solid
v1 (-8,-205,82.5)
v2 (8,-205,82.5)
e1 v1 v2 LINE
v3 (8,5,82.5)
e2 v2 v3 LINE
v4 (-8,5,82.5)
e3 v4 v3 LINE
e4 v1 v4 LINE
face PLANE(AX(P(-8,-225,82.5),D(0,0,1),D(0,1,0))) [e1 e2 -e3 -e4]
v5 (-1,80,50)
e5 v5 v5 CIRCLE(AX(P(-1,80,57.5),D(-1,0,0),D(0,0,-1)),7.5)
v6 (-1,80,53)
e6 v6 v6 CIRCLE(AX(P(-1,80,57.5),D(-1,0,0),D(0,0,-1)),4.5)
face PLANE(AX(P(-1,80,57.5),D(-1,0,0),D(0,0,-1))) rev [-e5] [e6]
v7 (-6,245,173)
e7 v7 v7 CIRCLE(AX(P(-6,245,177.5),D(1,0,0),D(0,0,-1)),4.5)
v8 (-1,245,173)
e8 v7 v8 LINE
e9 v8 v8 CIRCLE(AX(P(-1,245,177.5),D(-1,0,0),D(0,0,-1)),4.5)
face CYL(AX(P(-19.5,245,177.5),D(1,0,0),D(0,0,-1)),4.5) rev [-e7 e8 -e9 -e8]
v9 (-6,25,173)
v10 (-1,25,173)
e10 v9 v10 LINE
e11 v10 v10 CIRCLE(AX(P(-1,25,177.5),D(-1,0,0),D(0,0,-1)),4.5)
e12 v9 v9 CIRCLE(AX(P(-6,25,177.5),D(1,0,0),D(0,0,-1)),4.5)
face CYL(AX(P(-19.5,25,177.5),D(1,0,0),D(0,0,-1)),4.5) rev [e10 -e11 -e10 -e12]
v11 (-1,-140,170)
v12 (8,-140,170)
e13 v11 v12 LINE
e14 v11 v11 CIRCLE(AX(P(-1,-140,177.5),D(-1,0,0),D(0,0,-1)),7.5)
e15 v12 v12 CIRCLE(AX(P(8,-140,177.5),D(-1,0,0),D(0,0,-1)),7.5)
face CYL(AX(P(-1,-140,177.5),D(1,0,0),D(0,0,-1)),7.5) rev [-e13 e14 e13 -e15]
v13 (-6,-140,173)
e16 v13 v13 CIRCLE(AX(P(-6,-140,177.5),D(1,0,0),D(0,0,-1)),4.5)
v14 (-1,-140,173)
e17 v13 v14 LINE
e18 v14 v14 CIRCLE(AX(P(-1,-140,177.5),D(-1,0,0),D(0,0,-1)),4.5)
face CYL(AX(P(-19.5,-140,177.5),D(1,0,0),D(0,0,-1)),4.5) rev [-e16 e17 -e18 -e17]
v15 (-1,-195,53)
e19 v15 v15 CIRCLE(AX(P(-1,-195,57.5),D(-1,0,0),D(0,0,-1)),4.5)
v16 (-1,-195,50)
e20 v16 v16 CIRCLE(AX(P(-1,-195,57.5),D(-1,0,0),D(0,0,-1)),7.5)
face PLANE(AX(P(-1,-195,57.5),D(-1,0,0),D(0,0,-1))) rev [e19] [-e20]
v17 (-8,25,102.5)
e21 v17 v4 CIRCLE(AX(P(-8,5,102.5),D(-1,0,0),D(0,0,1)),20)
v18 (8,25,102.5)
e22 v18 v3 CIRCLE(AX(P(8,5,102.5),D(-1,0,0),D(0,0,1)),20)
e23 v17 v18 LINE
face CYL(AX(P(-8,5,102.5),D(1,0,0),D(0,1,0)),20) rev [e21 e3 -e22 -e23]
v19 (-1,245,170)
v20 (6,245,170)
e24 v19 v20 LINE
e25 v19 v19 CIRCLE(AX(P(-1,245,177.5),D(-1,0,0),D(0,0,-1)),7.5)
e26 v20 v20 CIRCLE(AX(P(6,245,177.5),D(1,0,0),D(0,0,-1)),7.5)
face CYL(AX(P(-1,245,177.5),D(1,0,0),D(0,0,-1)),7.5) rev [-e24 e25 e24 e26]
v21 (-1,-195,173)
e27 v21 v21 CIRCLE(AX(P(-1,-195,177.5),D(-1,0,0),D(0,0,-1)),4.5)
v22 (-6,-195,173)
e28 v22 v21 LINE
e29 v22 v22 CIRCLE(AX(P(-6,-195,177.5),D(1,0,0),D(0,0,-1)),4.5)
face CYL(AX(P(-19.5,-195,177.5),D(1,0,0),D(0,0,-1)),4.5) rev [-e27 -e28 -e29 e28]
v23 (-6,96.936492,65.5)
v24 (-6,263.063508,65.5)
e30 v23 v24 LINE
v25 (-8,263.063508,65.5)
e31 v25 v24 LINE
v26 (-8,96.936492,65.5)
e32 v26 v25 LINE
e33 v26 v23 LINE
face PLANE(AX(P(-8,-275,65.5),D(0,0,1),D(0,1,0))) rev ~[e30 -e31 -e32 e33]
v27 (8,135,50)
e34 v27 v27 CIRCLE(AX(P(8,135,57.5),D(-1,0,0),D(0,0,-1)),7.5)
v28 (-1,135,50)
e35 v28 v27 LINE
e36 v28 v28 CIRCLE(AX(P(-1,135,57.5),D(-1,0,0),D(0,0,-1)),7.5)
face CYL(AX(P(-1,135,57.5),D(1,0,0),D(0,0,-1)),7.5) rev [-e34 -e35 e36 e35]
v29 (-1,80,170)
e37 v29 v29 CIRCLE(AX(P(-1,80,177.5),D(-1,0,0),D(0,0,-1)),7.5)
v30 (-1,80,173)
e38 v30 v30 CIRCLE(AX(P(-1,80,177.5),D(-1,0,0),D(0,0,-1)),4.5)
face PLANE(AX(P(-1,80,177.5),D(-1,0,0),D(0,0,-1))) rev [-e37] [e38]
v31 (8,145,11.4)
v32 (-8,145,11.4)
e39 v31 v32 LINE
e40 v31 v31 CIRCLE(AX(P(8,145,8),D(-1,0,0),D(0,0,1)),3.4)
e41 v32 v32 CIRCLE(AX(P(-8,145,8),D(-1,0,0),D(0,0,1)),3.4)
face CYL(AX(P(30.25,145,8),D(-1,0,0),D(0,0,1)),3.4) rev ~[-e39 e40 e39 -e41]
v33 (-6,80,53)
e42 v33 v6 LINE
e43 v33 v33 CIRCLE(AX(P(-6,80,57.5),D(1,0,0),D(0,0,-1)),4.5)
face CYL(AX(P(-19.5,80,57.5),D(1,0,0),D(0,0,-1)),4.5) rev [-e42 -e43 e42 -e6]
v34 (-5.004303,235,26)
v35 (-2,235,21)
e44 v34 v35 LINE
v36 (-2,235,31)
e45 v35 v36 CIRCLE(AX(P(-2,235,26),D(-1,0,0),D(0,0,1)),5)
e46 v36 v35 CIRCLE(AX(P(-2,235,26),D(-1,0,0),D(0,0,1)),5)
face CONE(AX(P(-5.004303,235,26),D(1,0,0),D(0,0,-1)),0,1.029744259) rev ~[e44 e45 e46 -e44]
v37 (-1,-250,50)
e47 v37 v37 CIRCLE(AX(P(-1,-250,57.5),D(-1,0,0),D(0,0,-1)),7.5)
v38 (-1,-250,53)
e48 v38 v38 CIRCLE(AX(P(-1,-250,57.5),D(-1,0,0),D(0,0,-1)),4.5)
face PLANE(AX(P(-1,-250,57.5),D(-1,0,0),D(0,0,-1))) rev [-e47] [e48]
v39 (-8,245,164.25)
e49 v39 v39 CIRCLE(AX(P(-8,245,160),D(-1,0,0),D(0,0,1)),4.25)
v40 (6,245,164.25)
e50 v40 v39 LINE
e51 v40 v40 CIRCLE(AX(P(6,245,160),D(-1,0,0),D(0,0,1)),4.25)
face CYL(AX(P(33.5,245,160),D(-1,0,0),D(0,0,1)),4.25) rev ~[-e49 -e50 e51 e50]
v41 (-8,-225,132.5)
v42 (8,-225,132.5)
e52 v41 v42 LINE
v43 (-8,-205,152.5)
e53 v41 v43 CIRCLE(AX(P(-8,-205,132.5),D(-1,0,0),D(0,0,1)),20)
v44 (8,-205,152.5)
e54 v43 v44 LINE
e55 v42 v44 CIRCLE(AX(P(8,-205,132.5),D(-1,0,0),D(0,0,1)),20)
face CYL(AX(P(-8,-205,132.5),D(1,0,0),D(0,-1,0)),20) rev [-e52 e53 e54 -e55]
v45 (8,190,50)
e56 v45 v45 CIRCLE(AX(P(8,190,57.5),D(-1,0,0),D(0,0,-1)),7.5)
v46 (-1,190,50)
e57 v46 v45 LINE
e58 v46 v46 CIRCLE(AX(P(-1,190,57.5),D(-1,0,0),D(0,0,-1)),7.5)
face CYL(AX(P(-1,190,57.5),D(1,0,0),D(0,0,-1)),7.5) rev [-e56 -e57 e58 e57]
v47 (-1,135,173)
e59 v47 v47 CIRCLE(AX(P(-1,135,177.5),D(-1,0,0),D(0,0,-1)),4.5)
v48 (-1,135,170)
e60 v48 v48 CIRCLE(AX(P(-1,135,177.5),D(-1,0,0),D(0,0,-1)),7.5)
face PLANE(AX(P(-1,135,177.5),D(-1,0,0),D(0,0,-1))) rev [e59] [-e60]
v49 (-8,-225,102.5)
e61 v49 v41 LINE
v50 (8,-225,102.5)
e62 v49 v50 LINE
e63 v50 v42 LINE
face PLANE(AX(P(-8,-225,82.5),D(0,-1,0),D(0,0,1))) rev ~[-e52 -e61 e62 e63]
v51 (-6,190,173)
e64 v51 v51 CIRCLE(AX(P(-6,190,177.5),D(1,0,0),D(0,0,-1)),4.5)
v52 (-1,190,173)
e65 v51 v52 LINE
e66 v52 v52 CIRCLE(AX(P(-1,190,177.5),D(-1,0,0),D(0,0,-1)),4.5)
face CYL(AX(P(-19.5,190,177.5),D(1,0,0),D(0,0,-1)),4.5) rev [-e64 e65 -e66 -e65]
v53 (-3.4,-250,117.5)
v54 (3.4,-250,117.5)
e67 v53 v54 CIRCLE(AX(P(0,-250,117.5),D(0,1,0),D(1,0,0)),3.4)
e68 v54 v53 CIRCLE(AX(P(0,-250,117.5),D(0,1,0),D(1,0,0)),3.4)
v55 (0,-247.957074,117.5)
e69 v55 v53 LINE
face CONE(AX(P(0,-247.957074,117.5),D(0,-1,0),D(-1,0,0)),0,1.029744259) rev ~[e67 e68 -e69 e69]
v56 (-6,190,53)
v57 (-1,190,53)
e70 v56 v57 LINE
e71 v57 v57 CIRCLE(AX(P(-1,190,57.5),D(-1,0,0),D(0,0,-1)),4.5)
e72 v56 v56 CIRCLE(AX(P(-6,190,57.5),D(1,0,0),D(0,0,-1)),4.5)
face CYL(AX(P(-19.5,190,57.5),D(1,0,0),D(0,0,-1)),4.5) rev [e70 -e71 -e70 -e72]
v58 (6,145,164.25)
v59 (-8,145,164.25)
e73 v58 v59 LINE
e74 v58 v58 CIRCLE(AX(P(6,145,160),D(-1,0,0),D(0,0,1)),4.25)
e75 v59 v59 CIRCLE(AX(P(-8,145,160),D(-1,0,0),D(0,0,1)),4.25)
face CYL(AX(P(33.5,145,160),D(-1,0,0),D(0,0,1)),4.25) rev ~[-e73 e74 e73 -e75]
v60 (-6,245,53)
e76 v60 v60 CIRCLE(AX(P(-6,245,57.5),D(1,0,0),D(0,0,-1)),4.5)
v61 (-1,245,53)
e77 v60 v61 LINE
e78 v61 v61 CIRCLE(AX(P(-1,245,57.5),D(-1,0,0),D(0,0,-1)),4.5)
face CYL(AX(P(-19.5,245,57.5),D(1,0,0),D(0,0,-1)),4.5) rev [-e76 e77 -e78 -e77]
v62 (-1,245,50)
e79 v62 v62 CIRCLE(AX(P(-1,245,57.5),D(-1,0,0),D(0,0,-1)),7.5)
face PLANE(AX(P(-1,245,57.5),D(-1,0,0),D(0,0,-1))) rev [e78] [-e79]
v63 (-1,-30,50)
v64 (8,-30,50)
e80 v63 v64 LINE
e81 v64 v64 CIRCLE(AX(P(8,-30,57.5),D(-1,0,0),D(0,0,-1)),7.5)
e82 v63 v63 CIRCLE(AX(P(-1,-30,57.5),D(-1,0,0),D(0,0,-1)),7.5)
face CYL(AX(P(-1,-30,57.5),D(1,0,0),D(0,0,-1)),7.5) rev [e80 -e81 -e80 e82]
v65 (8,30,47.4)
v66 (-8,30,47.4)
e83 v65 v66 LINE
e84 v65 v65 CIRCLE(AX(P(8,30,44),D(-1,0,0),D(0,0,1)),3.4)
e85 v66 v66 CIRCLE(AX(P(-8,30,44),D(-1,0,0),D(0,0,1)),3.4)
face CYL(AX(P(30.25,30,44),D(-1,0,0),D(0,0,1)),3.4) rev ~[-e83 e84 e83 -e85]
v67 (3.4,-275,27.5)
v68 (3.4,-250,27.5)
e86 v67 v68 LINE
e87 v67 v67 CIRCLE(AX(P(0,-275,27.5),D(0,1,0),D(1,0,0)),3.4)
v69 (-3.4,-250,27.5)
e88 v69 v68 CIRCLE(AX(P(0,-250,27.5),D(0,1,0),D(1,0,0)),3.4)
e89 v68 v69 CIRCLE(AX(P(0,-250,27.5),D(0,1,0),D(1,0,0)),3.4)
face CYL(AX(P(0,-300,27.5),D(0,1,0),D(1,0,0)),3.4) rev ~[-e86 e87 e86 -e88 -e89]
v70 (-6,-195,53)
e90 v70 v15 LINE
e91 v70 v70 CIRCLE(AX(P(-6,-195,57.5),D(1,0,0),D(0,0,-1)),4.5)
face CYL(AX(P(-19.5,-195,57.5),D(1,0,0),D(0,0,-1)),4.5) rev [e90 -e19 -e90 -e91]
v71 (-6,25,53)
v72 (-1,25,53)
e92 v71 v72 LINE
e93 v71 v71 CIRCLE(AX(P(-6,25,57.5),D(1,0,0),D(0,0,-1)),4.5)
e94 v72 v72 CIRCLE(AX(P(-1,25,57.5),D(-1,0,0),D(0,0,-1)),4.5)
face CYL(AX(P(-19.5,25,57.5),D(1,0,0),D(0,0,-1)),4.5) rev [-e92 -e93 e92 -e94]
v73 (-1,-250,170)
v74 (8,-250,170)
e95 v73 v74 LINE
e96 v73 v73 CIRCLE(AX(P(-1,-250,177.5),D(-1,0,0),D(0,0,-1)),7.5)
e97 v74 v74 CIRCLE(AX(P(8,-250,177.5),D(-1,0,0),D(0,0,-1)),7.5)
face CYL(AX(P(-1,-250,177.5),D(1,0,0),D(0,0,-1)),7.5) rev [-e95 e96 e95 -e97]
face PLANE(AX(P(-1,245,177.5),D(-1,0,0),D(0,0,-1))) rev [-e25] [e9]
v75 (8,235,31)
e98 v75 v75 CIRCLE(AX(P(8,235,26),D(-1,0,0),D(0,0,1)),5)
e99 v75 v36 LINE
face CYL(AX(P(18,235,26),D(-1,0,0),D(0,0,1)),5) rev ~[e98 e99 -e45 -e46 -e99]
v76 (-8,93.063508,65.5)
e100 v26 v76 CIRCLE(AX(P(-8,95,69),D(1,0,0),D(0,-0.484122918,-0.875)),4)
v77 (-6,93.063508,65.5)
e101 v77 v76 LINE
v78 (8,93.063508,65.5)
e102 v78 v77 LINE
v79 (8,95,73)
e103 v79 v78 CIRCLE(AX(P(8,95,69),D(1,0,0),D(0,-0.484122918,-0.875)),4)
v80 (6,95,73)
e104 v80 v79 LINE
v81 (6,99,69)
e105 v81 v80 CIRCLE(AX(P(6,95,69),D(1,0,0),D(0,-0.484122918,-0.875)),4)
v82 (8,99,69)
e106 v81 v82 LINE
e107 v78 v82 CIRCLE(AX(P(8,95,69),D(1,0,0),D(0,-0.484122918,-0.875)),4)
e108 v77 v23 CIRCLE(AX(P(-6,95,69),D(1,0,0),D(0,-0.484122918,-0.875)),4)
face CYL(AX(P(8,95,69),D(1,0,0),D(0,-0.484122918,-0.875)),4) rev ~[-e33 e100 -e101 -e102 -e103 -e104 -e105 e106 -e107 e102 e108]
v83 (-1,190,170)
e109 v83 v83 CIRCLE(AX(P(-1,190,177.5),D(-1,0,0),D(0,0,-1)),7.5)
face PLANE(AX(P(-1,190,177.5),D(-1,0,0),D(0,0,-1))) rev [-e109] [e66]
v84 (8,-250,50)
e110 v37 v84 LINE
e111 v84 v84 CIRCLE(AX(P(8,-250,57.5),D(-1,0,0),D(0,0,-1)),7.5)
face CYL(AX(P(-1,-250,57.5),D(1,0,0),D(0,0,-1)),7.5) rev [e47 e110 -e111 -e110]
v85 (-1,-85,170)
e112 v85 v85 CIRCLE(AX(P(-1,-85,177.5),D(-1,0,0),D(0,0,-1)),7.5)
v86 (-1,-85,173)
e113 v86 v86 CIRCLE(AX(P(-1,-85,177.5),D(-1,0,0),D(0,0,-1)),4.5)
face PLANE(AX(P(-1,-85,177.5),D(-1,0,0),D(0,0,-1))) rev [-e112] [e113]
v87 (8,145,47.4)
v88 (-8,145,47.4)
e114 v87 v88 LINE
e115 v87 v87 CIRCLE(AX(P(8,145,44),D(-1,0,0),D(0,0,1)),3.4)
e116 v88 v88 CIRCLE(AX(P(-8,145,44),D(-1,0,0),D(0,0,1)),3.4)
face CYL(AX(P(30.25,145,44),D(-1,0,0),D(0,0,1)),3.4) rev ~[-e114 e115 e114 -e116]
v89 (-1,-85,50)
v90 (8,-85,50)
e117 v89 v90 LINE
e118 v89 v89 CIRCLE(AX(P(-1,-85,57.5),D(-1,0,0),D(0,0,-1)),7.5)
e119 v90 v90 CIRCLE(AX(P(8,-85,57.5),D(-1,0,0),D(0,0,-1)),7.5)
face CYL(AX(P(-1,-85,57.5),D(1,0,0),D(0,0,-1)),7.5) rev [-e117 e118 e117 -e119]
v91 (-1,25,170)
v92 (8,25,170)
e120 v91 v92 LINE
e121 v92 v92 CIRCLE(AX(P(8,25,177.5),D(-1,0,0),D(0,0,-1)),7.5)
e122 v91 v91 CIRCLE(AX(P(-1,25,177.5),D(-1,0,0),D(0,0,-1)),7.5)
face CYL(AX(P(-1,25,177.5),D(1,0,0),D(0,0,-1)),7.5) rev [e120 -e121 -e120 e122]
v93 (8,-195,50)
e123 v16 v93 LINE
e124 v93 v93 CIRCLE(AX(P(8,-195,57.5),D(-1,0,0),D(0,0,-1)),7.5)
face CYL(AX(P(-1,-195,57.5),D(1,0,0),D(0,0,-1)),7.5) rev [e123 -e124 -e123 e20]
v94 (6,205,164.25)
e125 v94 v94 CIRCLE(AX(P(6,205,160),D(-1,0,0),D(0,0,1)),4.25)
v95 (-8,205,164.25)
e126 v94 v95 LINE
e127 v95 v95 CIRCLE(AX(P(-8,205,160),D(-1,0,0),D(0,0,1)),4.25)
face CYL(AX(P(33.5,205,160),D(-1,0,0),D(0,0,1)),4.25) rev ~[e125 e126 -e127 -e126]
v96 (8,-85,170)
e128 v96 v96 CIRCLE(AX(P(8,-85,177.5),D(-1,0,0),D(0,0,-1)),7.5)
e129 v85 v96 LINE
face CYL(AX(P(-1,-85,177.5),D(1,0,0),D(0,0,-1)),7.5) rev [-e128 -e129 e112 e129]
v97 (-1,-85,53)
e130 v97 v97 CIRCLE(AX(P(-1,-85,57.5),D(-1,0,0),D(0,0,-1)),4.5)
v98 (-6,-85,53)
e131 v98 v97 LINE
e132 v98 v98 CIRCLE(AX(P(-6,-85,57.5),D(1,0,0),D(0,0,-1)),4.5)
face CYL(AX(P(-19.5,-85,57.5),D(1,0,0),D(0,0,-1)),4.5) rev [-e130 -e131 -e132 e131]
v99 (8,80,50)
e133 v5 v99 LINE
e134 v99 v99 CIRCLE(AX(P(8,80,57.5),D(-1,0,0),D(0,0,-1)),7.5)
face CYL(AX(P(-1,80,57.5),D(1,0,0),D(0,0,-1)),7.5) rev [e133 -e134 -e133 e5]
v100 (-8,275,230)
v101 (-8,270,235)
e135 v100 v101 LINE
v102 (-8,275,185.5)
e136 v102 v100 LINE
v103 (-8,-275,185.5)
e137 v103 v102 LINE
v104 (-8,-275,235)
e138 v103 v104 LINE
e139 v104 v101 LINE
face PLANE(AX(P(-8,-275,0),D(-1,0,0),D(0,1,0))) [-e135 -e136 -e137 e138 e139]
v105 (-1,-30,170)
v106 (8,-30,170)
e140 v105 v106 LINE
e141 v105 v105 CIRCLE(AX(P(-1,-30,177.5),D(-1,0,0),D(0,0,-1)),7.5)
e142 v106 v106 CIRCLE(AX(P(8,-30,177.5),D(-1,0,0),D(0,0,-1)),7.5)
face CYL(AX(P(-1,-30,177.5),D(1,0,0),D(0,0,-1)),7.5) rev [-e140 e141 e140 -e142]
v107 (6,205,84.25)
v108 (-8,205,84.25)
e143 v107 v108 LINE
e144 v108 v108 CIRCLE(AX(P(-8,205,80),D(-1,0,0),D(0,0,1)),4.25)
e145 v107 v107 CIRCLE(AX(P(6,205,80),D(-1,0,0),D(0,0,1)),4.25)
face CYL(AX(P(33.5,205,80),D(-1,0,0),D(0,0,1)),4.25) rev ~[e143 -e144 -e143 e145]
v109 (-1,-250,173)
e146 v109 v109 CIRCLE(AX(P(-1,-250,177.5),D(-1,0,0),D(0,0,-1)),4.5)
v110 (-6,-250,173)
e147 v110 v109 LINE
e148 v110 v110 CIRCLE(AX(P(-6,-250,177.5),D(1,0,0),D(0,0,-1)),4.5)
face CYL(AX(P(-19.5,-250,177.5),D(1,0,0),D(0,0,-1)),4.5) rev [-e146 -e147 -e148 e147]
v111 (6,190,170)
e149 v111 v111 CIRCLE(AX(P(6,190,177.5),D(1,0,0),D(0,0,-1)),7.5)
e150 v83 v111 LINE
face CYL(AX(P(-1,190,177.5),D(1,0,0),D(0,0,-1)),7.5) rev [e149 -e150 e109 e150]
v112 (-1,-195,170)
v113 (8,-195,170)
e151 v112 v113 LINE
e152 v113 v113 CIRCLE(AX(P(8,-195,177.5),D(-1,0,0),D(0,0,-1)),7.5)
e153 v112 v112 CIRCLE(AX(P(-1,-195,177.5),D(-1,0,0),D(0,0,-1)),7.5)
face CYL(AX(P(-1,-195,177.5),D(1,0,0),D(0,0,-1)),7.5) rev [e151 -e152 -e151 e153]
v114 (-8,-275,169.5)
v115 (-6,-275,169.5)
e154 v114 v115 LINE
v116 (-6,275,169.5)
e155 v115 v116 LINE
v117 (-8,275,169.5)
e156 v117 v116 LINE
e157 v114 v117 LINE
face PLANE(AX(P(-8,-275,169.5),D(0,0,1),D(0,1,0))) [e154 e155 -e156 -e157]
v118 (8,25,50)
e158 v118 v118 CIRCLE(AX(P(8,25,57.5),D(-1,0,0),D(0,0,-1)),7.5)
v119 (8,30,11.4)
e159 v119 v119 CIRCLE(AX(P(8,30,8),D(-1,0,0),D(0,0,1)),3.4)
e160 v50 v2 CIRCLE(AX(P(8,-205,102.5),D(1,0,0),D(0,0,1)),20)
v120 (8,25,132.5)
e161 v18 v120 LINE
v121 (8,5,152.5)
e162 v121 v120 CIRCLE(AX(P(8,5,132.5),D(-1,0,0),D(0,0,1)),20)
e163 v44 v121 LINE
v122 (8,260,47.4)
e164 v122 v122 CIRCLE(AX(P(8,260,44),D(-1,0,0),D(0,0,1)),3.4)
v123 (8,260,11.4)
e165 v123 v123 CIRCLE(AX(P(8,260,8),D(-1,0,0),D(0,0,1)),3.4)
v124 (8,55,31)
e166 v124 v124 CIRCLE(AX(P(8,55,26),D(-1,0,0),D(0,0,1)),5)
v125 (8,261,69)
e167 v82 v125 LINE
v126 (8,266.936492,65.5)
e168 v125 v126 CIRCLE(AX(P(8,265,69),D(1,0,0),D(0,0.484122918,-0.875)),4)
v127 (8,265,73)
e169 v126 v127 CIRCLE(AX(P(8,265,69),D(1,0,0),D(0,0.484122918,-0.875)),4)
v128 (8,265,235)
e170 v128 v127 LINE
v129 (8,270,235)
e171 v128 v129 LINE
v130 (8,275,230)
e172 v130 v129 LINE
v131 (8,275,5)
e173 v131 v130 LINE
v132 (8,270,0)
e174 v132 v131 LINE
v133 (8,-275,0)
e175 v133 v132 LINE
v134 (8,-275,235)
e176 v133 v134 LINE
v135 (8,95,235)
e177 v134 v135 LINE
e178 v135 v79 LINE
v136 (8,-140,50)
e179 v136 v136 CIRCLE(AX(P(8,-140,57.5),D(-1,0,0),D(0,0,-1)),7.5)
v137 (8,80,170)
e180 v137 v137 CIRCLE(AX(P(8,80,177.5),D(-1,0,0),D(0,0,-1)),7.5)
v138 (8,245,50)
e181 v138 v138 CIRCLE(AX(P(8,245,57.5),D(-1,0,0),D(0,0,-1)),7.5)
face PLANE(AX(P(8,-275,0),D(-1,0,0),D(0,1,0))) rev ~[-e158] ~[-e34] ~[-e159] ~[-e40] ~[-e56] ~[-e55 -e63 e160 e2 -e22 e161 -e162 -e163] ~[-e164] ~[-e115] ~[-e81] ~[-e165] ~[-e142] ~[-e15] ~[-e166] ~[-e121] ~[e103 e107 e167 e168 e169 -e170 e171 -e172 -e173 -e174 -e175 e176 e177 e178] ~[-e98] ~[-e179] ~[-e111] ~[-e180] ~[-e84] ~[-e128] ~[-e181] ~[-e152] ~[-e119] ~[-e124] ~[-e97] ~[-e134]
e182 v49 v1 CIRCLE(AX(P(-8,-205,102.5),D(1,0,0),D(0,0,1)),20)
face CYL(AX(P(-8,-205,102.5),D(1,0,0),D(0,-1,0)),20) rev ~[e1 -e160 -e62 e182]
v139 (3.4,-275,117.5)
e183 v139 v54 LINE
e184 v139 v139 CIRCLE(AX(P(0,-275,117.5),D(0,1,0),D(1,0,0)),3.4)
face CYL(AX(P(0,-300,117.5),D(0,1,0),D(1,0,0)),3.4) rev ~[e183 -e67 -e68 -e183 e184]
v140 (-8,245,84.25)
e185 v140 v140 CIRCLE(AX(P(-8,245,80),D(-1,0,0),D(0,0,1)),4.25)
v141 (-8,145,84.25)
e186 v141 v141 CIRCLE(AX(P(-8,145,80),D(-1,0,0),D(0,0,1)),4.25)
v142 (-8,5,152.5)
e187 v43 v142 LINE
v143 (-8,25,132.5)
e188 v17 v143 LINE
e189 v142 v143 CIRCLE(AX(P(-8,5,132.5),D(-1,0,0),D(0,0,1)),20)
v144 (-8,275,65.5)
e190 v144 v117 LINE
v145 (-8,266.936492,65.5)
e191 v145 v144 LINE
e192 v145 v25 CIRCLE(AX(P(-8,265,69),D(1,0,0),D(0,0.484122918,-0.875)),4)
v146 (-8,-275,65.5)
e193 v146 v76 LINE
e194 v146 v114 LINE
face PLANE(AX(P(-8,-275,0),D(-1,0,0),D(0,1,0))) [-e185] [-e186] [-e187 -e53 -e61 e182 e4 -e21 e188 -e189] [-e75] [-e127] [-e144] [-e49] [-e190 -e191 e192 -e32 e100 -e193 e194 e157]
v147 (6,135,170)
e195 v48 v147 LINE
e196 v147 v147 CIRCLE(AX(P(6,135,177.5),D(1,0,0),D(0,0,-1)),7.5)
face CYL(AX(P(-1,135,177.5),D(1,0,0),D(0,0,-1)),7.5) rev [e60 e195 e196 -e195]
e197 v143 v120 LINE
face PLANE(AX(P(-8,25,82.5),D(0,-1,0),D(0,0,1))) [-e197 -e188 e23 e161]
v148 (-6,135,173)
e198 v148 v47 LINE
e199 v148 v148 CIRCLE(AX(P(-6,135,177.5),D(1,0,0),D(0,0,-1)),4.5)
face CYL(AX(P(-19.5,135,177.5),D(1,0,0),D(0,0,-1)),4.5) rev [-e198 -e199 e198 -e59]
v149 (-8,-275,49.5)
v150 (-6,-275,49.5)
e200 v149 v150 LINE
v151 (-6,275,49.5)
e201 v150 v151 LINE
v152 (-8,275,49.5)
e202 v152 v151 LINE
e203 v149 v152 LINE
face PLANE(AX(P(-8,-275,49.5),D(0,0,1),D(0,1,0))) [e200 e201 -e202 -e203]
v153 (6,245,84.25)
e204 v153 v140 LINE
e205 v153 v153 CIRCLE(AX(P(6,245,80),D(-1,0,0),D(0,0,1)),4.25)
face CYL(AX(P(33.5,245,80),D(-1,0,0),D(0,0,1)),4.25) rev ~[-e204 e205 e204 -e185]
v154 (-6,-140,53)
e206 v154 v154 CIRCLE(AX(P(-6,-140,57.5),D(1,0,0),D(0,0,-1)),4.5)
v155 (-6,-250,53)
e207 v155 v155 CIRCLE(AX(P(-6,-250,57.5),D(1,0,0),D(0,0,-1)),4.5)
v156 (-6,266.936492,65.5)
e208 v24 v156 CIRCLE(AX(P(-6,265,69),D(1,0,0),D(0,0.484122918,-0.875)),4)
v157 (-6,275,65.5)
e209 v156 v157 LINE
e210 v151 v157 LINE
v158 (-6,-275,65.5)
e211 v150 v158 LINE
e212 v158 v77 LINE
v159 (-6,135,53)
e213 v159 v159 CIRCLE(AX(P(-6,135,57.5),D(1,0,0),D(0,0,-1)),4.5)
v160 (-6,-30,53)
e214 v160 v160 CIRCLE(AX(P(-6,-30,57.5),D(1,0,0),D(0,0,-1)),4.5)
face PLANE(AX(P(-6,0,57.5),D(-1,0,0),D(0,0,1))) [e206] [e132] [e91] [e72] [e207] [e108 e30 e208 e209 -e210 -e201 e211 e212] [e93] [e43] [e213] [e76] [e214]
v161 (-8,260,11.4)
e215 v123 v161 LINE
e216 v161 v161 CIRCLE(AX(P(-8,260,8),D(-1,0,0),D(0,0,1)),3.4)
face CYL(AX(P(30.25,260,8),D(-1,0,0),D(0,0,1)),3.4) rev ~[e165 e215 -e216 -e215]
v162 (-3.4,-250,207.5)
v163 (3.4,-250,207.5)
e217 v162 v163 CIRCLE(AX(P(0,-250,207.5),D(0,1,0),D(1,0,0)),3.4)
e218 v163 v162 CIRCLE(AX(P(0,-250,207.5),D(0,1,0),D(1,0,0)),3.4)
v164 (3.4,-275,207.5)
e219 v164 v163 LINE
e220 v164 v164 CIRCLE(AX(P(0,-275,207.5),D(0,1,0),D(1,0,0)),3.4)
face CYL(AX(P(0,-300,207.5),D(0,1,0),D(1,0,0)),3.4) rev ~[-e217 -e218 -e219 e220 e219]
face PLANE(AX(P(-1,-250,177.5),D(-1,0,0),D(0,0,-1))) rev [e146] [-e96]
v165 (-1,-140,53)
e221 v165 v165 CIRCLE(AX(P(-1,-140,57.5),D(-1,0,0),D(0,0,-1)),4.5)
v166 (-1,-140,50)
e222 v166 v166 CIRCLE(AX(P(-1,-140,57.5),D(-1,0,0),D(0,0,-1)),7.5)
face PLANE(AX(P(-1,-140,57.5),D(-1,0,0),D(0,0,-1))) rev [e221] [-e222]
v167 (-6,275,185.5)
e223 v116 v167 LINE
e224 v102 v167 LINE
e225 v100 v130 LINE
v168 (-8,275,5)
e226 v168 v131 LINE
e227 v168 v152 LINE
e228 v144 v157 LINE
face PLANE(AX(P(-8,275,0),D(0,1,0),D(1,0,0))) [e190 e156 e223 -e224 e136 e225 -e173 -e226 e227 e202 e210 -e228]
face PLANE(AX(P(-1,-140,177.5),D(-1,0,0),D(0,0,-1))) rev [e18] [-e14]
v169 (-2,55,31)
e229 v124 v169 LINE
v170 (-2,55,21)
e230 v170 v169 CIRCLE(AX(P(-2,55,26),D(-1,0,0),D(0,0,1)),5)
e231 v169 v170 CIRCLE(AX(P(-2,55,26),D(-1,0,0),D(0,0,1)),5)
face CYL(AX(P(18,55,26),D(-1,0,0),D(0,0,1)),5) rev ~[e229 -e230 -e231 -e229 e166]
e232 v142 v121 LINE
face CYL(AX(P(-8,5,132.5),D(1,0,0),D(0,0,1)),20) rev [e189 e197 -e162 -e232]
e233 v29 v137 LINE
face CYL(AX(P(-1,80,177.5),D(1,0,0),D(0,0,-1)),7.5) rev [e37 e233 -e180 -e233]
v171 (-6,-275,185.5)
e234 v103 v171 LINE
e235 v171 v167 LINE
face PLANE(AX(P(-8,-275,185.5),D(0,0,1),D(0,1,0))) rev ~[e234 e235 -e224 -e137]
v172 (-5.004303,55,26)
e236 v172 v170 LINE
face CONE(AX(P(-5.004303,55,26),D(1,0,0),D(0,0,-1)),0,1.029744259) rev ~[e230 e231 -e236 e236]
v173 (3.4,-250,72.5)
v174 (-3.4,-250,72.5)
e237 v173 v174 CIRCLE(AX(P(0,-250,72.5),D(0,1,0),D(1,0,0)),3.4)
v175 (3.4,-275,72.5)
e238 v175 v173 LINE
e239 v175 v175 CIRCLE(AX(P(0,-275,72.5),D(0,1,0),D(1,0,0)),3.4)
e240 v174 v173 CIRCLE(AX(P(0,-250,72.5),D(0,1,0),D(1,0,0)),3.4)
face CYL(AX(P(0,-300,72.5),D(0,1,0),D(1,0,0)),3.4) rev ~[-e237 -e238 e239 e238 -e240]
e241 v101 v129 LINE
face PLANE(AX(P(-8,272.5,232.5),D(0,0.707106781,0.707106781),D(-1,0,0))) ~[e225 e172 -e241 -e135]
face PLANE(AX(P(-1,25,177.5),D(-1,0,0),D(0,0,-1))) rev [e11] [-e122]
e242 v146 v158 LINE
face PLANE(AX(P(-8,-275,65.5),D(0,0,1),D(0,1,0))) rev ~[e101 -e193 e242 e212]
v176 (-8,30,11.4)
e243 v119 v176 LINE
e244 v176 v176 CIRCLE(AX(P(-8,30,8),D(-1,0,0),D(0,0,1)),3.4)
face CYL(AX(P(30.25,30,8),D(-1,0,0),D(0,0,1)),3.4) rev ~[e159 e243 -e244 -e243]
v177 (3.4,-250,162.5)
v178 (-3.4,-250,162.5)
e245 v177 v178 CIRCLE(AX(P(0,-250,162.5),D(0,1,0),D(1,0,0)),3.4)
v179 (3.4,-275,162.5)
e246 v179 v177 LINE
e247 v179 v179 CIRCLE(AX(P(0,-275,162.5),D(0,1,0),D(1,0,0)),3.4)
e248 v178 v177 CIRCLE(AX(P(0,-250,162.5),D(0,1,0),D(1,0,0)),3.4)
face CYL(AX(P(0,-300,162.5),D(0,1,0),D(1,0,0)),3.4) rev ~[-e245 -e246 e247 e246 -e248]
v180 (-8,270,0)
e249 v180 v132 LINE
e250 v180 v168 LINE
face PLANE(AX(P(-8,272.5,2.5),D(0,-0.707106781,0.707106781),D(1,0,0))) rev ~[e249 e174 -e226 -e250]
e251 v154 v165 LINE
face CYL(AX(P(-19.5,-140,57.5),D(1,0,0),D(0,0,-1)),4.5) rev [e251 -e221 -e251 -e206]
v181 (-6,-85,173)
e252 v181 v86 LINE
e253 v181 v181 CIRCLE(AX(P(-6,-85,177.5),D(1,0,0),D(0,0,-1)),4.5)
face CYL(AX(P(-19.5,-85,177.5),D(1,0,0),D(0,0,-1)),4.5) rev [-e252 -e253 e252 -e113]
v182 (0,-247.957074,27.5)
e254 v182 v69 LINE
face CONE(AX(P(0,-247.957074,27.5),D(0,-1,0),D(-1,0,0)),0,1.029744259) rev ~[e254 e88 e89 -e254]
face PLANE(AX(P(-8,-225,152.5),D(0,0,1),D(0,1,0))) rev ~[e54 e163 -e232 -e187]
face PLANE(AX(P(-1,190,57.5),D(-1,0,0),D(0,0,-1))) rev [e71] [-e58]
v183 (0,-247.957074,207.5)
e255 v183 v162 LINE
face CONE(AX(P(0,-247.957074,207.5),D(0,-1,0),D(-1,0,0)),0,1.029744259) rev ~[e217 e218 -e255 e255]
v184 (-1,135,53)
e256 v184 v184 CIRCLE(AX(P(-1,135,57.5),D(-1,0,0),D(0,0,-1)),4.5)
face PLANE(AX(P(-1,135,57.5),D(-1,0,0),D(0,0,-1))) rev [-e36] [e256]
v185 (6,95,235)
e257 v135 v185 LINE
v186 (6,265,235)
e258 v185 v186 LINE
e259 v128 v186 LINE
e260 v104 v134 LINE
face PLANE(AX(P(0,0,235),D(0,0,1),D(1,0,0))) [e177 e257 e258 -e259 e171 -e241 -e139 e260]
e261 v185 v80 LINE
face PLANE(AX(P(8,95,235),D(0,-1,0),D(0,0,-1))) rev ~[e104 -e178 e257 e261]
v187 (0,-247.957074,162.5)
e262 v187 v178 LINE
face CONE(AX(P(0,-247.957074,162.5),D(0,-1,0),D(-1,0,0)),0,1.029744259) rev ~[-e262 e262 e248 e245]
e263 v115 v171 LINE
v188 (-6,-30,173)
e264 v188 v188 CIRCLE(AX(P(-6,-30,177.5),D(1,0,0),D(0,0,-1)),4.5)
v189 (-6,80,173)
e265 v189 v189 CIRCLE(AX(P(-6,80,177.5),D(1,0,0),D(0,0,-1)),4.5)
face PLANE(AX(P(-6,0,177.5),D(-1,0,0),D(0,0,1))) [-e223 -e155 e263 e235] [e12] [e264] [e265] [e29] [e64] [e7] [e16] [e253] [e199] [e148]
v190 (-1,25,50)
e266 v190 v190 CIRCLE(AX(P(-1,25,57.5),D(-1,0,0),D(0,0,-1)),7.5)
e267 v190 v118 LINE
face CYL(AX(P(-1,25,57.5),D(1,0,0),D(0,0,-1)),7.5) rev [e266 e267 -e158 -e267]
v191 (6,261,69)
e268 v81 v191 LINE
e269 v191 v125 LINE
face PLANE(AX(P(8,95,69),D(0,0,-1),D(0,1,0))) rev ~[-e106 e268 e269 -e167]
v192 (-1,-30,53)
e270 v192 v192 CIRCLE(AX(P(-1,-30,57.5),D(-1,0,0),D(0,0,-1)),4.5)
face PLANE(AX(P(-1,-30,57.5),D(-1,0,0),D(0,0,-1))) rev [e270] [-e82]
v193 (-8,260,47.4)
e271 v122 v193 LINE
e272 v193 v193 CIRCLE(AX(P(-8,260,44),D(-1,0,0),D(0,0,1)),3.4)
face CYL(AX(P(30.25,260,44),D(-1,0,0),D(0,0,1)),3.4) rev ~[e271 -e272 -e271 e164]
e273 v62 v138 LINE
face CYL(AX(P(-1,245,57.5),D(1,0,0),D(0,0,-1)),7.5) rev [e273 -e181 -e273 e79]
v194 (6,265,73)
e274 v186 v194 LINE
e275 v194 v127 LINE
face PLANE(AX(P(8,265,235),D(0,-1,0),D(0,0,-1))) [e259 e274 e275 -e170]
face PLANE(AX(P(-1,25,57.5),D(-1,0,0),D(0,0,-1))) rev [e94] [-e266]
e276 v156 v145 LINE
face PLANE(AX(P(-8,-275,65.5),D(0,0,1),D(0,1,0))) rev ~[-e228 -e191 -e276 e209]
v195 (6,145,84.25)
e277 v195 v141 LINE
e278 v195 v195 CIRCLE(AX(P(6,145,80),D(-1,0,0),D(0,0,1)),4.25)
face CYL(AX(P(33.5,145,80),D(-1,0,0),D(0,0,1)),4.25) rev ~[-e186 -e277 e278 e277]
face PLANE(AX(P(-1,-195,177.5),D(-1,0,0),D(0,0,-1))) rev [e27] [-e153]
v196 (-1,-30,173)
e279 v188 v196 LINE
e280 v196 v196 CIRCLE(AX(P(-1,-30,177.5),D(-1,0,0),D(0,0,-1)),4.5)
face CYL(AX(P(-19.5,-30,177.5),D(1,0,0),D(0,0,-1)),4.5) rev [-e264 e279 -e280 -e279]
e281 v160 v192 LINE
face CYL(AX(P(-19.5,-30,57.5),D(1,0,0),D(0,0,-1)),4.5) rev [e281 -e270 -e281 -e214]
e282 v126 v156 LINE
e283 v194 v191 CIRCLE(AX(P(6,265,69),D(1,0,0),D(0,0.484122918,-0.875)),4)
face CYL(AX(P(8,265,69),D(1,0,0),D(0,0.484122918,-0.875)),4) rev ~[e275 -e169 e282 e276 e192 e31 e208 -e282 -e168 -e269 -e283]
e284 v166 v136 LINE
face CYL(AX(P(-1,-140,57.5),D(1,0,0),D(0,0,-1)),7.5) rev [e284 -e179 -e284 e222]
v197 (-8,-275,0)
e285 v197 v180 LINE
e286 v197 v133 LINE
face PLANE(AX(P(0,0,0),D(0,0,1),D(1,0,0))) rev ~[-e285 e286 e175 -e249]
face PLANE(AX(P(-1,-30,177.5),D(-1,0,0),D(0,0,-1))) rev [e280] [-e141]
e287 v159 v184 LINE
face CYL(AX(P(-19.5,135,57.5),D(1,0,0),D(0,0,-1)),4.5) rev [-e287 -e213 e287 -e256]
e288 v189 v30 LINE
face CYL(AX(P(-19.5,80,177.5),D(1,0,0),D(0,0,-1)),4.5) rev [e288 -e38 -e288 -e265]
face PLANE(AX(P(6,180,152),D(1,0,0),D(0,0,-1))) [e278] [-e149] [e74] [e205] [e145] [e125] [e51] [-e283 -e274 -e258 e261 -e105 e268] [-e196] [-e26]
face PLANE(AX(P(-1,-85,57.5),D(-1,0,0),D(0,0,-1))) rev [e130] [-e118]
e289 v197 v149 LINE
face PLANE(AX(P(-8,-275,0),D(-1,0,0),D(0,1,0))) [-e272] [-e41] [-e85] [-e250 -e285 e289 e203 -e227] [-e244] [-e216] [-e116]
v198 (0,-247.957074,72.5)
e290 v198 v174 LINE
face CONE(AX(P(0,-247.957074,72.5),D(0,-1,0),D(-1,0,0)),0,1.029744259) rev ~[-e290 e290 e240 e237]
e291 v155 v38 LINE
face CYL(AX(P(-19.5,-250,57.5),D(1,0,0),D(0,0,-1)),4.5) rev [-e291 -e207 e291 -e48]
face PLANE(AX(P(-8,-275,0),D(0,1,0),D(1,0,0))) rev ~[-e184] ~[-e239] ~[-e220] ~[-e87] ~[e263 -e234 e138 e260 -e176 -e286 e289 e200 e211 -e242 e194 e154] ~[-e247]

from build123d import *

# Parameters (mm, degrees)
SKETCH_1_W               = 16
SKETCH_1_H               = 550
EXTRUDE_1_DEPTH          = 235
SKETCH_4_W               = 16
SKETCH_4_H               = 550
CUT_EXTRUDE_3_DEPTH      = 2
SKETCH_5_W               = 166
SKETCH_5_H               = 170
CUT_EXTRUDE_4_DEPTH      = 2
HOLE_WIZARD_M10_1_D      = 8.5
HOLE_WIZARD_M10_1_DEPTH  = 27.5
HOLE_WIZARD_M10_1_TIP    = 2.553657631
HOLE_WIZARD_M8_1_D       = 6.8
HOLE_WIZARD_M8_1_DEPTH   = 25
HOLE_WIZARD_M8_1_TIP     = 2.042926105
SKETCH_15_W              = 70
SKETCH_15_H              = 250
CUT_EXTRUDE_5_DEPTH      = 16
FILLET_1_R               = 20
CHAMFER_1_SIZE           = 5
HOLE_WIZARD_1_AT_2_COUNT = 2
HOLE_WIZARD_1_AT_2_PITCH = 120
PATTERN_LINEAR_1_COUNT   = 10
PATTERN_LINEAR_1_PITCH   = 55
HOLE_WIZARD_M8_2_D       = 6.8
HOLE_WIZARD_M8_2_DEPTH   = 22.25
HOLE_WIZARD_M8_2_TIP     = 2.042926105
SKETCH_20_R              = 4
CUT_EXTRUDE_6_DEPTH      = 363.085625232
MM_1_D                   = 10
MM_1_DEPTH               = 10
MM_1_TIP                 = 3.004303095


with BuildPart() as part:
    # 草图1 → 凸台-拉伸1 (new body)
    with BuildSketch(Plane.XY):
        Rectangle(SKETCH_1_W, SKETCH_1_H)
    extrude(amount=EXTRUDE_1_DEPTH)

    # 草图4 → 切除-拉伸3 (cut)
    with BuildSketch(Plane.ZY.offset(8)):
        with Locations((57.5, 0)):
            Rectangle(SKETCH_4_W, SKETCH_4_H)
        with Locations((177.5, 0)):
            Rectangle(SKETCH_4_W, SKETCH_4_H)
    extrude(amount=-CUT_EXTRUDE_3_DEPTH, mode=Mode.SUBTRACT)

    # 草图5 → 切除-拉伸4 (cut)
    with BuildSketch(Plane(origin=(8, 0, 0), x_dir=(0, 0, -1), z_dir=(1, 0, 0))):
        with Locations((-152, 180)):
            Rectangle(SKETCH_5_W, SKETCH_5_H)
    extrude(amount=-CUT_EXTRUDE_4_DEPTH, mode=Mode.SUBTRACT)

    # M10 螺纹孔1
    with Locations(Plane(origin=(6, 0, 0), x_dir=(0, 0, -1), z_dir=(1, 0, 0))):
        with Locations((-160, 245), (-80, 145), (-160, 145), (-80, 245), (-80, 205), (-160, 205)):
            Hole(HOLE_WIZARD_M10_1_D / 2, depth=HOLE_WIZARD_M10_1_DEPTH)
            with Locations((0, 0, -(HOLE_WIZARD_M10_1_DEPTH + HOLE_WIZARD_M10_1_TIP / 2))):  # 118° drill point
                Cone(0, HOLE_WIZARD_M10_1_D / 2, HOLE_WIZARD_M10_1_TIP, mode=Mode.SUBTRACT)

    # M8 螺纹孔1
    with Locations(Plane(origin=(0, -275, 0), x_dir=(-1, 0, 0), z_dir=(0, -1, 0))):
        with Locations((0, -207.5), (0, -72.5), (0, -27.5), (0, -117.5), (0, -162.5)):
            Hole(HOLE_WIZARD_M8_1_D / 2, depth=HOLE_WIZARD_M8_1_DEPTH)
            with Locations((0, 0, -(HOLE_WIZARD_M8_1_DEPTH + HOLE_WIZARD_M8_1_TIP / 2))):  # 118° drill point
                Cone(0, HOLE_WIZARD_M8_1_D / 2, HOLE_WIZARD_M8_1_TIP, mode=Mode.SUBTRACT)

    # 草图15 → 切除-拉伸5 (cut)
    with BuildSketch(Plane.ZY.offset(8)):
        with Locations((117.5, -100)):
            Rectangle(SKETCH_15_W, SKETCH_15_H)
    extrude(amount=-CUT_EXTRUDE_5_DEPTH, mode=Mode.SUBTRACT)

    # 圆角1
    fillet_1_edges = [part.edges().sort_by_distance(p)[0] for p in [
        (0, 25, 152.5),
        (0, -225, 152.5),
        (0, -225, 82.5),
        (0, 25, 82.5),
    ]]
    fillet(fillet_1_edges, radius=FILLET_1_R)

    # 倒角1
    chamfer_1_edges = [part.edges().sort_by_distance(p)[0] for p in [
        (0, 275, 0),
        (0, 275, 235),
    ]]
    chamfer(chamfer_1_edges, length=CHAMFER_1_SIZE)

    # 草图17 → 打孔尺寸(%根据)内六角圆柱头螺钉的类型1 (revolve, cut)
    with BuildSketch(Plane(origin=(8, -250, 57.5), x_dir=(0, 0, -1), z_dir=(0, 1, 0))):
        Polygon((0, 0), (0, 30.203872786), (4.5, 27.5), (4.5, 9), (7.5, 9), (7.5, 0), align=None)
    hole_wizard_1 = revolve(axis=Axis((14.35, -250, 57.5), (-1, 0, 0)), mode=Mode.SUBTRACT)

    # 打孔尺寸(%根据)内六角圆柱头螺钉的类型1 at 2: 打孔尺寸(%根据)内六角圆柱头螺钉的类型1 ×2
    with Locations(*[(0, 0, i * HOLE_WIZARD_1_AT_2_PITCH) for i in range(1, HOLE_WIZARD_1_AT_2_COUNT)]):
        add(hole_wizard_1, mode=Mode.SUBTRACT)

    # 阵列(线性)1: 打孔尺寸(%根据)内六角圆柱头螺钉的类型1 ×10
    with Locations(*[(0, i * PATTERN_LINEAR_1_PITCH, 0) for i in range(1, PATTERN_LINEAR_1_COUNT)]):
        add(hole_wizard_1, mode=Mode.SUBTRACT)

    # 阵列(线性)1 copy 1 sketch → 阵列(线性)1 copy 1 (revolve, cut)
    with BuildSketch(Plane(origin=(8, -195, 177.5), x_dir=(0, 0, -1), z_dir=(0, 1, 0))):
        Polygon((0, 0), (0, 30.203872786), (4.5, 27.5), (4.5, 9), (7.5, 9), (7.5, 0), align=None)
    revolve(axis=Axis((14.35, -195, 177.5), (-1, 0, 0)), mode=Mode.SUBTRACT)

    # 阵列(线性)1 copy 2 sketch → 阵列(线性)1 copy 2 (revolve, cut)
    with BuildSketch(Plane(origin=(8, -140, 177.5), x_dir=(0, 0, -1), z_dir=(0, 1, 0))):
        Polygon((0, 0), (0, 30.203872786), (4.5, 27.5), (4.5, 9), (7.5, 9), (7.5, 0), align=None)
    revolve(axis=Axis((14.35, -140, 177.5), (-1, 0, 0)), mode=Mode.SUBTRACT)

    # 阵列(线性)1 copy 3 sketch → 阵列(线性)1 copy 3 (revolve, cut)
    with BuildSketch(Plane(origin=(8, -85, 177.5), x_dir=(0, 0, -1), z_dir=(0, 1, 0))):
        Polygon((0, 0), (0, 30.203872786), (4.5, 27.5), (4.5, 9), (7.5, 9), (7.5, 0), align=None)
    revolve(axis=Axis((14.35, -85, 177.5), (-1, 0, 0)), mode=Mode.SUBTRACT)

    # 阵列(线性)1 copy 4 sketch → 阵列(线性)1 copy 4 (revolve, cut)
    with BuildSketch(Plane(origin=(8, -30, 177.5), x_dir=(0, 0, -1), z_dir=(0, 1, 0))):
        Polygon((0, 0), (0, 30.203872786), (4.5, 27.5), (4.5, 9), (7.5, 9), (7.5, 0), align=None)
    revolve(axis=Axis((14.35, -30, 177.5), (-1, 0, 0)), mode=Mode.SUBTRACT)

    # 阵列(线性)1 copy 5 sketch → 阵列(线性)1 copy 5 (revolve, cut)
    with BuildSketch(Plane(origin=(8, 25, 177.5), x_dir=(0, 0, -1), z_dir=(0, 1, 0))):
        Polygon((0, 0), (0, 30.203872786), (4.5, 27.5), (4.5, 9), (7.5, 9), (7.5, 0), align=None)
    revolve(axis=Axis((14.35, 25, 177.5), (-1, 0, 0)), mode=Mode.SUBTRACT)

    # 阵列(线性)1 copy 6 sketch → 阵列(线性)1 copy 6 (revolve, cut)
    with BuildSketch(Plane(origin=(8, 80, 177.5), x_dir=(0, 0, -1), z_dir=(0, 1, 0))):
        Polygon((0, 0), (0, 30.203872786), (4.5, 27.5), (4.5, 9), (7.5, 9), (7.5, 0), align=None)
    revolve(axis=Axis((14.35, 80, 177.5), (-1, 0, 0)), mode=Mode.SUBTRACT)

    # 阵列(线性)1 copy 7 sketch → 阵列(线性)1 copy 7 (revolve, cut)
    with BuildSketch(Plane(origin=(8, 135, 177.5), x_dir=(0, 0, -1), z_dir=(0, 1, 0))):
        Polygon((0, 0), (0, 30.203872786), (4.5, 27.5), (4.5, 9), (7.5, 9), (7.5, 0), align=None)
    revolve(axis=Axis((14.35, 135, 177.5), (-1, 0, 0)), mode=Mode.SUBTRACT)

    # 阵列(线性)1 copy 8 sketch → 阵列(线性)1 copy 8 (revolve, cut)
    with BuildSketch(Plane(origin=(8, 190, 177.5), x_dir=(0, 0, -1), z_dir=(0, 1, 0))):
        Polygon((0, 0), (0, 30.203872786), (4.5, 27.5), (4.5, 9), (7.5, 9), (7.5, 0), align=None)
    revolve(axis=Axis((14.35, 190, 177.5), (-1, 0, 0)), mode=Mode.SUBTRACT)

    # 阵列(线性)1 copy 9 sketch → 阵列(线性)1 copy 9 (revolve, cut)
    with BuildSketch(Plane(origin=(8, 245, 177.5), x_dir=(0, 0, -1), z_dir=(0, 1, 0))):
        Polygon((0, 0), (0, 30.203872786), (4.5, 27.5), (4.5, 9), (7.5, 9), (7.5, 0), align=None)
    revolve(axis=Axis((14.35, 245, 177.5), (-1, 0, 0)), mode=Mode.SUBTRACT)

    # M8 螺纹孔2
    with Locations(Plane(origin=(8, 0, 0), x_dir=(0, 0, -1), z_dir=(1, 0, 0))):
        with Locations((-8, 145), (-44, 145), (-8, 260), (-44, 260), (-8, 30), (-44, 30)):
            Hole(HOLE_WIZARD_M8_2_D / 2, depth=HOLE_WIZARD_M8_2_DEPTH)
            with Locations((0, 0, -(HOLE_WIZARD_M8_2_DEPTH + HOLE_WIZARD_M8_2_TIP / 2))):  # 118° drill point
                Cone(0, HOLE_WIZARD_M8_2_D / 2, HOLE_WIZARD_M8_2_TIP, mode=Mode.SUBTRACT)

    # 草图20 → 切除-拉伸6 (cut, through all)
    with BuildSketch(Plane(origin=(8, 0, 0), x_dir=(0, 0, -1), z_dir=(1, 0, 0))):
        with Locations(Location((-69, 95, 0), (0, 0, 331.044975628))):
            Circle(SKETCH_20_R)
        with Locations(Location((-69, 265, 0), (0, 0, 28.955024372))):
            Circle(SKETCH_20_R)
    extrude(amount=-CUT_EXTRUDE_6_DEPTH, mode=Mode.SUBTRACT)

    # 大小mm 暗销孔1
    with Locations(Plane(origin=(8, 0, 0), x_dir=(0, 0, -1), z_dir=(1, 0, 0))):
        with Locations((-26, 235), (-26, 55)):
            Hole(MM_1_D / 2, depth=MM_1_DEPTH)
            with Locations((0, 0, -(MM_1_DEPTH + MM_1_TIP / 2))):  # 118° drill point
                Cone(0, MM_1_D / 2, MM_1_TIP, mode=Mode.SUBTRACT)


solid = part.part
